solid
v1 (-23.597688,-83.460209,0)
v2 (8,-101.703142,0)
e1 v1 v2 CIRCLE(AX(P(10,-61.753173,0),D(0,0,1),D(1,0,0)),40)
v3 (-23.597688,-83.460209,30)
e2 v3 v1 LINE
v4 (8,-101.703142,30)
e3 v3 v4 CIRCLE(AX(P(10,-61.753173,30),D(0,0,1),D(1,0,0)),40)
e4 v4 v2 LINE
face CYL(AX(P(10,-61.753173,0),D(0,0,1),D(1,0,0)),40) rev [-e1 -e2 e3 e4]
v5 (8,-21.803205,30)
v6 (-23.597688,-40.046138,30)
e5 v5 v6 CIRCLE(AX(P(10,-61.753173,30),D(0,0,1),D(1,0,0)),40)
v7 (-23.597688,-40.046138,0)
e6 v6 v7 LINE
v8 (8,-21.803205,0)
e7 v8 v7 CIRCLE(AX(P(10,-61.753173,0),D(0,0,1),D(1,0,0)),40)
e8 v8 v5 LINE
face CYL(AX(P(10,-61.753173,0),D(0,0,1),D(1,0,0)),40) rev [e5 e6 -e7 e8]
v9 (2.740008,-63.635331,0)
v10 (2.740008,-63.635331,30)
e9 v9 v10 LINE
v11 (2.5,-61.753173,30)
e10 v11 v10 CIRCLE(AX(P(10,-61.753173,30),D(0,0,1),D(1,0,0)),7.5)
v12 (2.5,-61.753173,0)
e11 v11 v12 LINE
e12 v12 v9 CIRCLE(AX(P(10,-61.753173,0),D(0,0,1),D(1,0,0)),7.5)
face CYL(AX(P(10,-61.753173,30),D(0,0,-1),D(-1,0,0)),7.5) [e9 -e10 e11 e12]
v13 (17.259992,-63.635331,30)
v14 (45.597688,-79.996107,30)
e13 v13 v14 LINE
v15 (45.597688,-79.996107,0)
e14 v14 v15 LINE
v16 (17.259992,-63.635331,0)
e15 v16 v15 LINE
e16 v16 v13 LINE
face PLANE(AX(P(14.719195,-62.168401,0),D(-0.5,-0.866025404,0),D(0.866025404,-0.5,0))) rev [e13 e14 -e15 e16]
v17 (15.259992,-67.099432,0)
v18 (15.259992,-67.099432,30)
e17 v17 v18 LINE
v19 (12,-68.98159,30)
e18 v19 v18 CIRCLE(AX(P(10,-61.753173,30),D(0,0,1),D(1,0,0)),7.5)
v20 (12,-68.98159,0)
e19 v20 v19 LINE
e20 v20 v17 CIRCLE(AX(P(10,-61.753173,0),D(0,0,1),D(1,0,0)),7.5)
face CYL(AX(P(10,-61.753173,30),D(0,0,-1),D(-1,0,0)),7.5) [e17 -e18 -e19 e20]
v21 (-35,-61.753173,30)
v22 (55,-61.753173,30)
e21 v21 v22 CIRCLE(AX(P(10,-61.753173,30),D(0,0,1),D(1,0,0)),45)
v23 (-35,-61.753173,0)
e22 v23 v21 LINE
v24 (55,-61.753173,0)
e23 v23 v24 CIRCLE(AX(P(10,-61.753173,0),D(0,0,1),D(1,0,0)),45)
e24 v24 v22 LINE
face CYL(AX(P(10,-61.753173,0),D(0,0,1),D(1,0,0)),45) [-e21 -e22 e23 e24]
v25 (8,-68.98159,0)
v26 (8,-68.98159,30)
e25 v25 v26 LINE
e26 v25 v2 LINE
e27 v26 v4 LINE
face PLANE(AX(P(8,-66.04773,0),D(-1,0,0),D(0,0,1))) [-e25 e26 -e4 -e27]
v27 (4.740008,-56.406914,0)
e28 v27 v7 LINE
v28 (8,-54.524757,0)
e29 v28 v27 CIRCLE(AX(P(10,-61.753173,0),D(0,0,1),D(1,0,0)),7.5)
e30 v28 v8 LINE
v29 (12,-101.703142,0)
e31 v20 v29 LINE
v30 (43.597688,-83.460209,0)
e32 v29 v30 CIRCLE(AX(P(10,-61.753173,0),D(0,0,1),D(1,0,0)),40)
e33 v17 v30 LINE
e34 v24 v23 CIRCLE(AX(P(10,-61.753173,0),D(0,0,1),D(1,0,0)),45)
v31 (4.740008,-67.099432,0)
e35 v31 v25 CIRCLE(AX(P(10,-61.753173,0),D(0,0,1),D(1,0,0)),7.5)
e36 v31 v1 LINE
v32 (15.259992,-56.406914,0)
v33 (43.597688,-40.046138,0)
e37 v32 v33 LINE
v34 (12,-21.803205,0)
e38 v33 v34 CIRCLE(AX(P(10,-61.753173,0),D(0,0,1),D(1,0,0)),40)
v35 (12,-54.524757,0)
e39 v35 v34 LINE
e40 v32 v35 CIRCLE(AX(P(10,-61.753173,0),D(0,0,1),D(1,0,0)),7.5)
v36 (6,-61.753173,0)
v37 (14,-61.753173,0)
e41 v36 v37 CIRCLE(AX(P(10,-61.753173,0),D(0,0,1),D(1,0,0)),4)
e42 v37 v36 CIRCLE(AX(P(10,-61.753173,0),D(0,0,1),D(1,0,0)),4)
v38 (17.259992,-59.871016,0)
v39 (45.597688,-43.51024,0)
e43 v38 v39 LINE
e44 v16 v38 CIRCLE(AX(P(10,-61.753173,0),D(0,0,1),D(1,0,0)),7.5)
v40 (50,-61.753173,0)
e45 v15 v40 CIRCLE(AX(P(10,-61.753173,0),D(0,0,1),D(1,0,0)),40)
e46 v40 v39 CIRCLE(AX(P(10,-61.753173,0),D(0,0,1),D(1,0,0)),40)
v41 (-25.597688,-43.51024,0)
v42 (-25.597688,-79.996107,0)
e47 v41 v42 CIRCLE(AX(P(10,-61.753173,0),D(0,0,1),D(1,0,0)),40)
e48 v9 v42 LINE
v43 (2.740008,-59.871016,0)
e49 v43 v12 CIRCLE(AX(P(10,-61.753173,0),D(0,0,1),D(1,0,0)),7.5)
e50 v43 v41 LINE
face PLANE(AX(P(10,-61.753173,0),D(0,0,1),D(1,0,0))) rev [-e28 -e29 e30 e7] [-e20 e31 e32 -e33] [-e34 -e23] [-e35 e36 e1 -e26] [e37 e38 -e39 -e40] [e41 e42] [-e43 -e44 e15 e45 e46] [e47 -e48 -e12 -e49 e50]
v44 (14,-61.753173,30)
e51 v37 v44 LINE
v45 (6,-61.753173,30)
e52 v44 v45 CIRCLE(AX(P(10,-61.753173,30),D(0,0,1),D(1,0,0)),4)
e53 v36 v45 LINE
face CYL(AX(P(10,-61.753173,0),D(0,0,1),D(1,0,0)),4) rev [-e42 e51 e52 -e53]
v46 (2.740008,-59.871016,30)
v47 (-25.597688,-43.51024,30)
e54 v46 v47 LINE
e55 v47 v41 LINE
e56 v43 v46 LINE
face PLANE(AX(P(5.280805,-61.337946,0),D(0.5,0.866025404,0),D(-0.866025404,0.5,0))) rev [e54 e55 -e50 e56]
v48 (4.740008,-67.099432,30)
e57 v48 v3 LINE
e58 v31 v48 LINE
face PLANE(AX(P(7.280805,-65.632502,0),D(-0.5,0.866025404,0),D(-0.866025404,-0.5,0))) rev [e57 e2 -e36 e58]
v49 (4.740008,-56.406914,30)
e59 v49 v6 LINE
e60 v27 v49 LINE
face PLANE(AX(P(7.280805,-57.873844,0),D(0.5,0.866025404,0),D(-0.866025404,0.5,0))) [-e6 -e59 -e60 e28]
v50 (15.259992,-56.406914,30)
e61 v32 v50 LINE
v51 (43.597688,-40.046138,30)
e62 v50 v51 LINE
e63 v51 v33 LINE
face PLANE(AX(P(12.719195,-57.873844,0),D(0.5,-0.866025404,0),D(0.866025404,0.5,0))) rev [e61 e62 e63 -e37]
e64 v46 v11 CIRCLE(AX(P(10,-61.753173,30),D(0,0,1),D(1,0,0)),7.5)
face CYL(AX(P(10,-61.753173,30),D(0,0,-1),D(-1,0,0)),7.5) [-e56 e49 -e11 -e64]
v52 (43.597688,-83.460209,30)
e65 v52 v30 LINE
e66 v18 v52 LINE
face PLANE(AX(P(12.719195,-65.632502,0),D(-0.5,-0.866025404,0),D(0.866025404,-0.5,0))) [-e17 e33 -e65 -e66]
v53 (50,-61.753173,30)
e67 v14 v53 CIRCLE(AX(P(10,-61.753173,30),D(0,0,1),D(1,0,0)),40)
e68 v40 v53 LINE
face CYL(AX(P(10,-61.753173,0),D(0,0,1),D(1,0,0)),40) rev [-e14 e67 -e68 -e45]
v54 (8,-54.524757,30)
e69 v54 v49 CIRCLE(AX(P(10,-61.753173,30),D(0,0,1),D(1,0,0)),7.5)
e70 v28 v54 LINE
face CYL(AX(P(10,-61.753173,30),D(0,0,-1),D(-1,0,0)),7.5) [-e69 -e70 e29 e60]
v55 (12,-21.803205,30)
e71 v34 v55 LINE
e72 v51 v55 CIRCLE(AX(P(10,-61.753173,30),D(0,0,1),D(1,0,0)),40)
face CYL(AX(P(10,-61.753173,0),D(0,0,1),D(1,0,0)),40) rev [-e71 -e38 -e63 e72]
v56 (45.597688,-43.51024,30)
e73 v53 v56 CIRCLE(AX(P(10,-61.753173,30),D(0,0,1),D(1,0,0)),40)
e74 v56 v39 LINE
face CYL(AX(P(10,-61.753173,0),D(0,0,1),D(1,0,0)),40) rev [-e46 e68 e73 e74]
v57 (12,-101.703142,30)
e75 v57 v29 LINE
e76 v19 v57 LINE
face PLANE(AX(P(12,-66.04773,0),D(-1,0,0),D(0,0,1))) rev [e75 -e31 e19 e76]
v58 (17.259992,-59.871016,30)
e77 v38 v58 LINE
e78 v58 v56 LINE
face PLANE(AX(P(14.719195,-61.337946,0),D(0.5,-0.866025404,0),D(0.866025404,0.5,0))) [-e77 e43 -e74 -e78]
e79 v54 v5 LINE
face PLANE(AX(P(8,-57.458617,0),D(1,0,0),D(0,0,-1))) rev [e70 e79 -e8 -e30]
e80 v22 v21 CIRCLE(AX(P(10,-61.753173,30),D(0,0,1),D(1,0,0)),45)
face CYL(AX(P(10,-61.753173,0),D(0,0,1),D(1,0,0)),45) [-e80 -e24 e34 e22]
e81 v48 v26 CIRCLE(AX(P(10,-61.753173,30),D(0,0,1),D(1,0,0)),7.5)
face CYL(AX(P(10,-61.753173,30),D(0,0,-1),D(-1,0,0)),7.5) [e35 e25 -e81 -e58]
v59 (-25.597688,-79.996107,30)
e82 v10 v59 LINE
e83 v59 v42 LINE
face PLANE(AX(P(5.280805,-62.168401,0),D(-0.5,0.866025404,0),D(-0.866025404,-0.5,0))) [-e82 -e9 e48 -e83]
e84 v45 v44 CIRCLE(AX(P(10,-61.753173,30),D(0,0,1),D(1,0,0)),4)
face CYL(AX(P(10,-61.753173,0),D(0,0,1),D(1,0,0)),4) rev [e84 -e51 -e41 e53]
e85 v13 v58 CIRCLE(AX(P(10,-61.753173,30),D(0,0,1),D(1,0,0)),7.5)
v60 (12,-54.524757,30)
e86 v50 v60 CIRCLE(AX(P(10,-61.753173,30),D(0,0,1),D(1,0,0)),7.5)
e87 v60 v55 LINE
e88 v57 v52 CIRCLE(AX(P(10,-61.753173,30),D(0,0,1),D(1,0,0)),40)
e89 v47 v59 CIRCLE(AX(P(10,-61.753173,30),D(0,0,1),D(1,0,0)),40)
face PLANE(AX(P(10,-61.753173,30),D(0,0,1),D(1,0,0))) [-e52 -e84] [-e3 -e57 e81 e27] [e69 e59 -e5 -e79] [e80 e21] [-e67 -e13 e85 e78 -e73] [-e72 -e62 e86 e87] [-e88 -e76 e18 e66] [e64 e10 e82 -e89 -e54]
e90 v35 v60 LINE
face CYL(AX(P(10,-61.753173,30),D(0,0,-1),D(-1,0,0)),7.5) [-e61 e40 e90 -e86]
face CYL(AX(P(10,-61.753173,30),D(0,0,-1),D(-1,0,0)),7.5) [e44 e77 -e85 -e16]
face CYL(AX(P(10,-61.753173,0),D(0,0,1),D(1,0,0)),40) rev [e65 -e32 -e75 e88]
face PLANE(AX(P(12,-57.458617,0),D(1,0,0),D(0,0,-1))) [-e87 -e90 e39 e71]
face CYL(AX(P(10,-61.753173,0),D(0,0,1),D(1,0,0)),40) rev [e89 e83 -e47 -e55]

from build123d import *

# Parameters (mm, degrees)
SKETCH1_R               = 7.5
BOSS_EXTRUDE1_DEPTH     = 30
SKETCH2_R               = 45
SKETCH2_R_2             = 40
EXTRUDE_THIN1_DEPTH     = 30
SKETCH5_W               = 4
SKETCH5_H               = 36.329230713
EXTRUDE_THIN3_DEPTH     = 30
CIRPATTERN4_COUNT       = 6
CUT_EXTRUDE1_DEPTH      = 124.778996688
CUT_EXTRUDE1_DEPTH_BACK = 124.778996688
SKETCH6_R               = 4


with BuildPart() as part:
    # Sketch1 → Boss-Extrude1 (new body)
    with BuildSketch(Plane.XY):
        with Locations((10, -61.753173354)):
            Circle(SKETCH1_R)
    extrude(amount=BOSS_EXTRUDE1_DEPTH)



with BuildPart() as body_2:
    # Sketch2 → Extrude-Thin1 (new body)
    with BuildSketch(Plane.XY.offset(30)):
        with Locations((10, -61.753173354)):
            Circle(SKETCH2_R)
        with Locations((10, -61.753173354)):
            Circle(SKETCH2_R_2, mode=Mode.SUBTRACT)
    extrude(amount=-EXTRUDE_THIN1_DEPTH)


with BuildPart() as part_1:
    add(part.part)

    add(body_2.part)  # Extrude-Thin3 merges body 2
    # Sketch5 → Extrude-Thin3 (add)
    with BuildSketch(Plane.XY.offset(30)):
        with Locations((10, -39.294001794)):
            Rectangle(SKETCH5_W, SKETCH5_H)
    extrude_thin3 = extrude(amount=-EXTRUDE_THIN3_DEPTH)

    # CirPattern4: Extrude-Thin3 ×6 about axis
    cirpattern4_axis = Axis((10, -61.753173354, 0), (0, 0, 1))
    for i in range(1, CIRPATTERN4_COUNT):
        add(extrude_thin3.rotate(cirpattern4_axis, i * 360 / CIRPATTERN4_COUNT))

    # Sketch6 → Cut-Extrude1 (cut, two sides: drawn at the far end of the back side and taken through both)
    with BuildSketch(Plane.XY.offset(30).offset(-CUT_EXTRUDE1_DEPTH_BACK)):
        with Locations((10, -61.753173354)):
            Circle(SKETCH6_R)
    extrude(amount=CUT_EXTRUDE1_DEPTH + CUT_EXTRUDE1_DEPTH_BACK, mode=Mode.SUBTRACT)


solid = part_1.part
